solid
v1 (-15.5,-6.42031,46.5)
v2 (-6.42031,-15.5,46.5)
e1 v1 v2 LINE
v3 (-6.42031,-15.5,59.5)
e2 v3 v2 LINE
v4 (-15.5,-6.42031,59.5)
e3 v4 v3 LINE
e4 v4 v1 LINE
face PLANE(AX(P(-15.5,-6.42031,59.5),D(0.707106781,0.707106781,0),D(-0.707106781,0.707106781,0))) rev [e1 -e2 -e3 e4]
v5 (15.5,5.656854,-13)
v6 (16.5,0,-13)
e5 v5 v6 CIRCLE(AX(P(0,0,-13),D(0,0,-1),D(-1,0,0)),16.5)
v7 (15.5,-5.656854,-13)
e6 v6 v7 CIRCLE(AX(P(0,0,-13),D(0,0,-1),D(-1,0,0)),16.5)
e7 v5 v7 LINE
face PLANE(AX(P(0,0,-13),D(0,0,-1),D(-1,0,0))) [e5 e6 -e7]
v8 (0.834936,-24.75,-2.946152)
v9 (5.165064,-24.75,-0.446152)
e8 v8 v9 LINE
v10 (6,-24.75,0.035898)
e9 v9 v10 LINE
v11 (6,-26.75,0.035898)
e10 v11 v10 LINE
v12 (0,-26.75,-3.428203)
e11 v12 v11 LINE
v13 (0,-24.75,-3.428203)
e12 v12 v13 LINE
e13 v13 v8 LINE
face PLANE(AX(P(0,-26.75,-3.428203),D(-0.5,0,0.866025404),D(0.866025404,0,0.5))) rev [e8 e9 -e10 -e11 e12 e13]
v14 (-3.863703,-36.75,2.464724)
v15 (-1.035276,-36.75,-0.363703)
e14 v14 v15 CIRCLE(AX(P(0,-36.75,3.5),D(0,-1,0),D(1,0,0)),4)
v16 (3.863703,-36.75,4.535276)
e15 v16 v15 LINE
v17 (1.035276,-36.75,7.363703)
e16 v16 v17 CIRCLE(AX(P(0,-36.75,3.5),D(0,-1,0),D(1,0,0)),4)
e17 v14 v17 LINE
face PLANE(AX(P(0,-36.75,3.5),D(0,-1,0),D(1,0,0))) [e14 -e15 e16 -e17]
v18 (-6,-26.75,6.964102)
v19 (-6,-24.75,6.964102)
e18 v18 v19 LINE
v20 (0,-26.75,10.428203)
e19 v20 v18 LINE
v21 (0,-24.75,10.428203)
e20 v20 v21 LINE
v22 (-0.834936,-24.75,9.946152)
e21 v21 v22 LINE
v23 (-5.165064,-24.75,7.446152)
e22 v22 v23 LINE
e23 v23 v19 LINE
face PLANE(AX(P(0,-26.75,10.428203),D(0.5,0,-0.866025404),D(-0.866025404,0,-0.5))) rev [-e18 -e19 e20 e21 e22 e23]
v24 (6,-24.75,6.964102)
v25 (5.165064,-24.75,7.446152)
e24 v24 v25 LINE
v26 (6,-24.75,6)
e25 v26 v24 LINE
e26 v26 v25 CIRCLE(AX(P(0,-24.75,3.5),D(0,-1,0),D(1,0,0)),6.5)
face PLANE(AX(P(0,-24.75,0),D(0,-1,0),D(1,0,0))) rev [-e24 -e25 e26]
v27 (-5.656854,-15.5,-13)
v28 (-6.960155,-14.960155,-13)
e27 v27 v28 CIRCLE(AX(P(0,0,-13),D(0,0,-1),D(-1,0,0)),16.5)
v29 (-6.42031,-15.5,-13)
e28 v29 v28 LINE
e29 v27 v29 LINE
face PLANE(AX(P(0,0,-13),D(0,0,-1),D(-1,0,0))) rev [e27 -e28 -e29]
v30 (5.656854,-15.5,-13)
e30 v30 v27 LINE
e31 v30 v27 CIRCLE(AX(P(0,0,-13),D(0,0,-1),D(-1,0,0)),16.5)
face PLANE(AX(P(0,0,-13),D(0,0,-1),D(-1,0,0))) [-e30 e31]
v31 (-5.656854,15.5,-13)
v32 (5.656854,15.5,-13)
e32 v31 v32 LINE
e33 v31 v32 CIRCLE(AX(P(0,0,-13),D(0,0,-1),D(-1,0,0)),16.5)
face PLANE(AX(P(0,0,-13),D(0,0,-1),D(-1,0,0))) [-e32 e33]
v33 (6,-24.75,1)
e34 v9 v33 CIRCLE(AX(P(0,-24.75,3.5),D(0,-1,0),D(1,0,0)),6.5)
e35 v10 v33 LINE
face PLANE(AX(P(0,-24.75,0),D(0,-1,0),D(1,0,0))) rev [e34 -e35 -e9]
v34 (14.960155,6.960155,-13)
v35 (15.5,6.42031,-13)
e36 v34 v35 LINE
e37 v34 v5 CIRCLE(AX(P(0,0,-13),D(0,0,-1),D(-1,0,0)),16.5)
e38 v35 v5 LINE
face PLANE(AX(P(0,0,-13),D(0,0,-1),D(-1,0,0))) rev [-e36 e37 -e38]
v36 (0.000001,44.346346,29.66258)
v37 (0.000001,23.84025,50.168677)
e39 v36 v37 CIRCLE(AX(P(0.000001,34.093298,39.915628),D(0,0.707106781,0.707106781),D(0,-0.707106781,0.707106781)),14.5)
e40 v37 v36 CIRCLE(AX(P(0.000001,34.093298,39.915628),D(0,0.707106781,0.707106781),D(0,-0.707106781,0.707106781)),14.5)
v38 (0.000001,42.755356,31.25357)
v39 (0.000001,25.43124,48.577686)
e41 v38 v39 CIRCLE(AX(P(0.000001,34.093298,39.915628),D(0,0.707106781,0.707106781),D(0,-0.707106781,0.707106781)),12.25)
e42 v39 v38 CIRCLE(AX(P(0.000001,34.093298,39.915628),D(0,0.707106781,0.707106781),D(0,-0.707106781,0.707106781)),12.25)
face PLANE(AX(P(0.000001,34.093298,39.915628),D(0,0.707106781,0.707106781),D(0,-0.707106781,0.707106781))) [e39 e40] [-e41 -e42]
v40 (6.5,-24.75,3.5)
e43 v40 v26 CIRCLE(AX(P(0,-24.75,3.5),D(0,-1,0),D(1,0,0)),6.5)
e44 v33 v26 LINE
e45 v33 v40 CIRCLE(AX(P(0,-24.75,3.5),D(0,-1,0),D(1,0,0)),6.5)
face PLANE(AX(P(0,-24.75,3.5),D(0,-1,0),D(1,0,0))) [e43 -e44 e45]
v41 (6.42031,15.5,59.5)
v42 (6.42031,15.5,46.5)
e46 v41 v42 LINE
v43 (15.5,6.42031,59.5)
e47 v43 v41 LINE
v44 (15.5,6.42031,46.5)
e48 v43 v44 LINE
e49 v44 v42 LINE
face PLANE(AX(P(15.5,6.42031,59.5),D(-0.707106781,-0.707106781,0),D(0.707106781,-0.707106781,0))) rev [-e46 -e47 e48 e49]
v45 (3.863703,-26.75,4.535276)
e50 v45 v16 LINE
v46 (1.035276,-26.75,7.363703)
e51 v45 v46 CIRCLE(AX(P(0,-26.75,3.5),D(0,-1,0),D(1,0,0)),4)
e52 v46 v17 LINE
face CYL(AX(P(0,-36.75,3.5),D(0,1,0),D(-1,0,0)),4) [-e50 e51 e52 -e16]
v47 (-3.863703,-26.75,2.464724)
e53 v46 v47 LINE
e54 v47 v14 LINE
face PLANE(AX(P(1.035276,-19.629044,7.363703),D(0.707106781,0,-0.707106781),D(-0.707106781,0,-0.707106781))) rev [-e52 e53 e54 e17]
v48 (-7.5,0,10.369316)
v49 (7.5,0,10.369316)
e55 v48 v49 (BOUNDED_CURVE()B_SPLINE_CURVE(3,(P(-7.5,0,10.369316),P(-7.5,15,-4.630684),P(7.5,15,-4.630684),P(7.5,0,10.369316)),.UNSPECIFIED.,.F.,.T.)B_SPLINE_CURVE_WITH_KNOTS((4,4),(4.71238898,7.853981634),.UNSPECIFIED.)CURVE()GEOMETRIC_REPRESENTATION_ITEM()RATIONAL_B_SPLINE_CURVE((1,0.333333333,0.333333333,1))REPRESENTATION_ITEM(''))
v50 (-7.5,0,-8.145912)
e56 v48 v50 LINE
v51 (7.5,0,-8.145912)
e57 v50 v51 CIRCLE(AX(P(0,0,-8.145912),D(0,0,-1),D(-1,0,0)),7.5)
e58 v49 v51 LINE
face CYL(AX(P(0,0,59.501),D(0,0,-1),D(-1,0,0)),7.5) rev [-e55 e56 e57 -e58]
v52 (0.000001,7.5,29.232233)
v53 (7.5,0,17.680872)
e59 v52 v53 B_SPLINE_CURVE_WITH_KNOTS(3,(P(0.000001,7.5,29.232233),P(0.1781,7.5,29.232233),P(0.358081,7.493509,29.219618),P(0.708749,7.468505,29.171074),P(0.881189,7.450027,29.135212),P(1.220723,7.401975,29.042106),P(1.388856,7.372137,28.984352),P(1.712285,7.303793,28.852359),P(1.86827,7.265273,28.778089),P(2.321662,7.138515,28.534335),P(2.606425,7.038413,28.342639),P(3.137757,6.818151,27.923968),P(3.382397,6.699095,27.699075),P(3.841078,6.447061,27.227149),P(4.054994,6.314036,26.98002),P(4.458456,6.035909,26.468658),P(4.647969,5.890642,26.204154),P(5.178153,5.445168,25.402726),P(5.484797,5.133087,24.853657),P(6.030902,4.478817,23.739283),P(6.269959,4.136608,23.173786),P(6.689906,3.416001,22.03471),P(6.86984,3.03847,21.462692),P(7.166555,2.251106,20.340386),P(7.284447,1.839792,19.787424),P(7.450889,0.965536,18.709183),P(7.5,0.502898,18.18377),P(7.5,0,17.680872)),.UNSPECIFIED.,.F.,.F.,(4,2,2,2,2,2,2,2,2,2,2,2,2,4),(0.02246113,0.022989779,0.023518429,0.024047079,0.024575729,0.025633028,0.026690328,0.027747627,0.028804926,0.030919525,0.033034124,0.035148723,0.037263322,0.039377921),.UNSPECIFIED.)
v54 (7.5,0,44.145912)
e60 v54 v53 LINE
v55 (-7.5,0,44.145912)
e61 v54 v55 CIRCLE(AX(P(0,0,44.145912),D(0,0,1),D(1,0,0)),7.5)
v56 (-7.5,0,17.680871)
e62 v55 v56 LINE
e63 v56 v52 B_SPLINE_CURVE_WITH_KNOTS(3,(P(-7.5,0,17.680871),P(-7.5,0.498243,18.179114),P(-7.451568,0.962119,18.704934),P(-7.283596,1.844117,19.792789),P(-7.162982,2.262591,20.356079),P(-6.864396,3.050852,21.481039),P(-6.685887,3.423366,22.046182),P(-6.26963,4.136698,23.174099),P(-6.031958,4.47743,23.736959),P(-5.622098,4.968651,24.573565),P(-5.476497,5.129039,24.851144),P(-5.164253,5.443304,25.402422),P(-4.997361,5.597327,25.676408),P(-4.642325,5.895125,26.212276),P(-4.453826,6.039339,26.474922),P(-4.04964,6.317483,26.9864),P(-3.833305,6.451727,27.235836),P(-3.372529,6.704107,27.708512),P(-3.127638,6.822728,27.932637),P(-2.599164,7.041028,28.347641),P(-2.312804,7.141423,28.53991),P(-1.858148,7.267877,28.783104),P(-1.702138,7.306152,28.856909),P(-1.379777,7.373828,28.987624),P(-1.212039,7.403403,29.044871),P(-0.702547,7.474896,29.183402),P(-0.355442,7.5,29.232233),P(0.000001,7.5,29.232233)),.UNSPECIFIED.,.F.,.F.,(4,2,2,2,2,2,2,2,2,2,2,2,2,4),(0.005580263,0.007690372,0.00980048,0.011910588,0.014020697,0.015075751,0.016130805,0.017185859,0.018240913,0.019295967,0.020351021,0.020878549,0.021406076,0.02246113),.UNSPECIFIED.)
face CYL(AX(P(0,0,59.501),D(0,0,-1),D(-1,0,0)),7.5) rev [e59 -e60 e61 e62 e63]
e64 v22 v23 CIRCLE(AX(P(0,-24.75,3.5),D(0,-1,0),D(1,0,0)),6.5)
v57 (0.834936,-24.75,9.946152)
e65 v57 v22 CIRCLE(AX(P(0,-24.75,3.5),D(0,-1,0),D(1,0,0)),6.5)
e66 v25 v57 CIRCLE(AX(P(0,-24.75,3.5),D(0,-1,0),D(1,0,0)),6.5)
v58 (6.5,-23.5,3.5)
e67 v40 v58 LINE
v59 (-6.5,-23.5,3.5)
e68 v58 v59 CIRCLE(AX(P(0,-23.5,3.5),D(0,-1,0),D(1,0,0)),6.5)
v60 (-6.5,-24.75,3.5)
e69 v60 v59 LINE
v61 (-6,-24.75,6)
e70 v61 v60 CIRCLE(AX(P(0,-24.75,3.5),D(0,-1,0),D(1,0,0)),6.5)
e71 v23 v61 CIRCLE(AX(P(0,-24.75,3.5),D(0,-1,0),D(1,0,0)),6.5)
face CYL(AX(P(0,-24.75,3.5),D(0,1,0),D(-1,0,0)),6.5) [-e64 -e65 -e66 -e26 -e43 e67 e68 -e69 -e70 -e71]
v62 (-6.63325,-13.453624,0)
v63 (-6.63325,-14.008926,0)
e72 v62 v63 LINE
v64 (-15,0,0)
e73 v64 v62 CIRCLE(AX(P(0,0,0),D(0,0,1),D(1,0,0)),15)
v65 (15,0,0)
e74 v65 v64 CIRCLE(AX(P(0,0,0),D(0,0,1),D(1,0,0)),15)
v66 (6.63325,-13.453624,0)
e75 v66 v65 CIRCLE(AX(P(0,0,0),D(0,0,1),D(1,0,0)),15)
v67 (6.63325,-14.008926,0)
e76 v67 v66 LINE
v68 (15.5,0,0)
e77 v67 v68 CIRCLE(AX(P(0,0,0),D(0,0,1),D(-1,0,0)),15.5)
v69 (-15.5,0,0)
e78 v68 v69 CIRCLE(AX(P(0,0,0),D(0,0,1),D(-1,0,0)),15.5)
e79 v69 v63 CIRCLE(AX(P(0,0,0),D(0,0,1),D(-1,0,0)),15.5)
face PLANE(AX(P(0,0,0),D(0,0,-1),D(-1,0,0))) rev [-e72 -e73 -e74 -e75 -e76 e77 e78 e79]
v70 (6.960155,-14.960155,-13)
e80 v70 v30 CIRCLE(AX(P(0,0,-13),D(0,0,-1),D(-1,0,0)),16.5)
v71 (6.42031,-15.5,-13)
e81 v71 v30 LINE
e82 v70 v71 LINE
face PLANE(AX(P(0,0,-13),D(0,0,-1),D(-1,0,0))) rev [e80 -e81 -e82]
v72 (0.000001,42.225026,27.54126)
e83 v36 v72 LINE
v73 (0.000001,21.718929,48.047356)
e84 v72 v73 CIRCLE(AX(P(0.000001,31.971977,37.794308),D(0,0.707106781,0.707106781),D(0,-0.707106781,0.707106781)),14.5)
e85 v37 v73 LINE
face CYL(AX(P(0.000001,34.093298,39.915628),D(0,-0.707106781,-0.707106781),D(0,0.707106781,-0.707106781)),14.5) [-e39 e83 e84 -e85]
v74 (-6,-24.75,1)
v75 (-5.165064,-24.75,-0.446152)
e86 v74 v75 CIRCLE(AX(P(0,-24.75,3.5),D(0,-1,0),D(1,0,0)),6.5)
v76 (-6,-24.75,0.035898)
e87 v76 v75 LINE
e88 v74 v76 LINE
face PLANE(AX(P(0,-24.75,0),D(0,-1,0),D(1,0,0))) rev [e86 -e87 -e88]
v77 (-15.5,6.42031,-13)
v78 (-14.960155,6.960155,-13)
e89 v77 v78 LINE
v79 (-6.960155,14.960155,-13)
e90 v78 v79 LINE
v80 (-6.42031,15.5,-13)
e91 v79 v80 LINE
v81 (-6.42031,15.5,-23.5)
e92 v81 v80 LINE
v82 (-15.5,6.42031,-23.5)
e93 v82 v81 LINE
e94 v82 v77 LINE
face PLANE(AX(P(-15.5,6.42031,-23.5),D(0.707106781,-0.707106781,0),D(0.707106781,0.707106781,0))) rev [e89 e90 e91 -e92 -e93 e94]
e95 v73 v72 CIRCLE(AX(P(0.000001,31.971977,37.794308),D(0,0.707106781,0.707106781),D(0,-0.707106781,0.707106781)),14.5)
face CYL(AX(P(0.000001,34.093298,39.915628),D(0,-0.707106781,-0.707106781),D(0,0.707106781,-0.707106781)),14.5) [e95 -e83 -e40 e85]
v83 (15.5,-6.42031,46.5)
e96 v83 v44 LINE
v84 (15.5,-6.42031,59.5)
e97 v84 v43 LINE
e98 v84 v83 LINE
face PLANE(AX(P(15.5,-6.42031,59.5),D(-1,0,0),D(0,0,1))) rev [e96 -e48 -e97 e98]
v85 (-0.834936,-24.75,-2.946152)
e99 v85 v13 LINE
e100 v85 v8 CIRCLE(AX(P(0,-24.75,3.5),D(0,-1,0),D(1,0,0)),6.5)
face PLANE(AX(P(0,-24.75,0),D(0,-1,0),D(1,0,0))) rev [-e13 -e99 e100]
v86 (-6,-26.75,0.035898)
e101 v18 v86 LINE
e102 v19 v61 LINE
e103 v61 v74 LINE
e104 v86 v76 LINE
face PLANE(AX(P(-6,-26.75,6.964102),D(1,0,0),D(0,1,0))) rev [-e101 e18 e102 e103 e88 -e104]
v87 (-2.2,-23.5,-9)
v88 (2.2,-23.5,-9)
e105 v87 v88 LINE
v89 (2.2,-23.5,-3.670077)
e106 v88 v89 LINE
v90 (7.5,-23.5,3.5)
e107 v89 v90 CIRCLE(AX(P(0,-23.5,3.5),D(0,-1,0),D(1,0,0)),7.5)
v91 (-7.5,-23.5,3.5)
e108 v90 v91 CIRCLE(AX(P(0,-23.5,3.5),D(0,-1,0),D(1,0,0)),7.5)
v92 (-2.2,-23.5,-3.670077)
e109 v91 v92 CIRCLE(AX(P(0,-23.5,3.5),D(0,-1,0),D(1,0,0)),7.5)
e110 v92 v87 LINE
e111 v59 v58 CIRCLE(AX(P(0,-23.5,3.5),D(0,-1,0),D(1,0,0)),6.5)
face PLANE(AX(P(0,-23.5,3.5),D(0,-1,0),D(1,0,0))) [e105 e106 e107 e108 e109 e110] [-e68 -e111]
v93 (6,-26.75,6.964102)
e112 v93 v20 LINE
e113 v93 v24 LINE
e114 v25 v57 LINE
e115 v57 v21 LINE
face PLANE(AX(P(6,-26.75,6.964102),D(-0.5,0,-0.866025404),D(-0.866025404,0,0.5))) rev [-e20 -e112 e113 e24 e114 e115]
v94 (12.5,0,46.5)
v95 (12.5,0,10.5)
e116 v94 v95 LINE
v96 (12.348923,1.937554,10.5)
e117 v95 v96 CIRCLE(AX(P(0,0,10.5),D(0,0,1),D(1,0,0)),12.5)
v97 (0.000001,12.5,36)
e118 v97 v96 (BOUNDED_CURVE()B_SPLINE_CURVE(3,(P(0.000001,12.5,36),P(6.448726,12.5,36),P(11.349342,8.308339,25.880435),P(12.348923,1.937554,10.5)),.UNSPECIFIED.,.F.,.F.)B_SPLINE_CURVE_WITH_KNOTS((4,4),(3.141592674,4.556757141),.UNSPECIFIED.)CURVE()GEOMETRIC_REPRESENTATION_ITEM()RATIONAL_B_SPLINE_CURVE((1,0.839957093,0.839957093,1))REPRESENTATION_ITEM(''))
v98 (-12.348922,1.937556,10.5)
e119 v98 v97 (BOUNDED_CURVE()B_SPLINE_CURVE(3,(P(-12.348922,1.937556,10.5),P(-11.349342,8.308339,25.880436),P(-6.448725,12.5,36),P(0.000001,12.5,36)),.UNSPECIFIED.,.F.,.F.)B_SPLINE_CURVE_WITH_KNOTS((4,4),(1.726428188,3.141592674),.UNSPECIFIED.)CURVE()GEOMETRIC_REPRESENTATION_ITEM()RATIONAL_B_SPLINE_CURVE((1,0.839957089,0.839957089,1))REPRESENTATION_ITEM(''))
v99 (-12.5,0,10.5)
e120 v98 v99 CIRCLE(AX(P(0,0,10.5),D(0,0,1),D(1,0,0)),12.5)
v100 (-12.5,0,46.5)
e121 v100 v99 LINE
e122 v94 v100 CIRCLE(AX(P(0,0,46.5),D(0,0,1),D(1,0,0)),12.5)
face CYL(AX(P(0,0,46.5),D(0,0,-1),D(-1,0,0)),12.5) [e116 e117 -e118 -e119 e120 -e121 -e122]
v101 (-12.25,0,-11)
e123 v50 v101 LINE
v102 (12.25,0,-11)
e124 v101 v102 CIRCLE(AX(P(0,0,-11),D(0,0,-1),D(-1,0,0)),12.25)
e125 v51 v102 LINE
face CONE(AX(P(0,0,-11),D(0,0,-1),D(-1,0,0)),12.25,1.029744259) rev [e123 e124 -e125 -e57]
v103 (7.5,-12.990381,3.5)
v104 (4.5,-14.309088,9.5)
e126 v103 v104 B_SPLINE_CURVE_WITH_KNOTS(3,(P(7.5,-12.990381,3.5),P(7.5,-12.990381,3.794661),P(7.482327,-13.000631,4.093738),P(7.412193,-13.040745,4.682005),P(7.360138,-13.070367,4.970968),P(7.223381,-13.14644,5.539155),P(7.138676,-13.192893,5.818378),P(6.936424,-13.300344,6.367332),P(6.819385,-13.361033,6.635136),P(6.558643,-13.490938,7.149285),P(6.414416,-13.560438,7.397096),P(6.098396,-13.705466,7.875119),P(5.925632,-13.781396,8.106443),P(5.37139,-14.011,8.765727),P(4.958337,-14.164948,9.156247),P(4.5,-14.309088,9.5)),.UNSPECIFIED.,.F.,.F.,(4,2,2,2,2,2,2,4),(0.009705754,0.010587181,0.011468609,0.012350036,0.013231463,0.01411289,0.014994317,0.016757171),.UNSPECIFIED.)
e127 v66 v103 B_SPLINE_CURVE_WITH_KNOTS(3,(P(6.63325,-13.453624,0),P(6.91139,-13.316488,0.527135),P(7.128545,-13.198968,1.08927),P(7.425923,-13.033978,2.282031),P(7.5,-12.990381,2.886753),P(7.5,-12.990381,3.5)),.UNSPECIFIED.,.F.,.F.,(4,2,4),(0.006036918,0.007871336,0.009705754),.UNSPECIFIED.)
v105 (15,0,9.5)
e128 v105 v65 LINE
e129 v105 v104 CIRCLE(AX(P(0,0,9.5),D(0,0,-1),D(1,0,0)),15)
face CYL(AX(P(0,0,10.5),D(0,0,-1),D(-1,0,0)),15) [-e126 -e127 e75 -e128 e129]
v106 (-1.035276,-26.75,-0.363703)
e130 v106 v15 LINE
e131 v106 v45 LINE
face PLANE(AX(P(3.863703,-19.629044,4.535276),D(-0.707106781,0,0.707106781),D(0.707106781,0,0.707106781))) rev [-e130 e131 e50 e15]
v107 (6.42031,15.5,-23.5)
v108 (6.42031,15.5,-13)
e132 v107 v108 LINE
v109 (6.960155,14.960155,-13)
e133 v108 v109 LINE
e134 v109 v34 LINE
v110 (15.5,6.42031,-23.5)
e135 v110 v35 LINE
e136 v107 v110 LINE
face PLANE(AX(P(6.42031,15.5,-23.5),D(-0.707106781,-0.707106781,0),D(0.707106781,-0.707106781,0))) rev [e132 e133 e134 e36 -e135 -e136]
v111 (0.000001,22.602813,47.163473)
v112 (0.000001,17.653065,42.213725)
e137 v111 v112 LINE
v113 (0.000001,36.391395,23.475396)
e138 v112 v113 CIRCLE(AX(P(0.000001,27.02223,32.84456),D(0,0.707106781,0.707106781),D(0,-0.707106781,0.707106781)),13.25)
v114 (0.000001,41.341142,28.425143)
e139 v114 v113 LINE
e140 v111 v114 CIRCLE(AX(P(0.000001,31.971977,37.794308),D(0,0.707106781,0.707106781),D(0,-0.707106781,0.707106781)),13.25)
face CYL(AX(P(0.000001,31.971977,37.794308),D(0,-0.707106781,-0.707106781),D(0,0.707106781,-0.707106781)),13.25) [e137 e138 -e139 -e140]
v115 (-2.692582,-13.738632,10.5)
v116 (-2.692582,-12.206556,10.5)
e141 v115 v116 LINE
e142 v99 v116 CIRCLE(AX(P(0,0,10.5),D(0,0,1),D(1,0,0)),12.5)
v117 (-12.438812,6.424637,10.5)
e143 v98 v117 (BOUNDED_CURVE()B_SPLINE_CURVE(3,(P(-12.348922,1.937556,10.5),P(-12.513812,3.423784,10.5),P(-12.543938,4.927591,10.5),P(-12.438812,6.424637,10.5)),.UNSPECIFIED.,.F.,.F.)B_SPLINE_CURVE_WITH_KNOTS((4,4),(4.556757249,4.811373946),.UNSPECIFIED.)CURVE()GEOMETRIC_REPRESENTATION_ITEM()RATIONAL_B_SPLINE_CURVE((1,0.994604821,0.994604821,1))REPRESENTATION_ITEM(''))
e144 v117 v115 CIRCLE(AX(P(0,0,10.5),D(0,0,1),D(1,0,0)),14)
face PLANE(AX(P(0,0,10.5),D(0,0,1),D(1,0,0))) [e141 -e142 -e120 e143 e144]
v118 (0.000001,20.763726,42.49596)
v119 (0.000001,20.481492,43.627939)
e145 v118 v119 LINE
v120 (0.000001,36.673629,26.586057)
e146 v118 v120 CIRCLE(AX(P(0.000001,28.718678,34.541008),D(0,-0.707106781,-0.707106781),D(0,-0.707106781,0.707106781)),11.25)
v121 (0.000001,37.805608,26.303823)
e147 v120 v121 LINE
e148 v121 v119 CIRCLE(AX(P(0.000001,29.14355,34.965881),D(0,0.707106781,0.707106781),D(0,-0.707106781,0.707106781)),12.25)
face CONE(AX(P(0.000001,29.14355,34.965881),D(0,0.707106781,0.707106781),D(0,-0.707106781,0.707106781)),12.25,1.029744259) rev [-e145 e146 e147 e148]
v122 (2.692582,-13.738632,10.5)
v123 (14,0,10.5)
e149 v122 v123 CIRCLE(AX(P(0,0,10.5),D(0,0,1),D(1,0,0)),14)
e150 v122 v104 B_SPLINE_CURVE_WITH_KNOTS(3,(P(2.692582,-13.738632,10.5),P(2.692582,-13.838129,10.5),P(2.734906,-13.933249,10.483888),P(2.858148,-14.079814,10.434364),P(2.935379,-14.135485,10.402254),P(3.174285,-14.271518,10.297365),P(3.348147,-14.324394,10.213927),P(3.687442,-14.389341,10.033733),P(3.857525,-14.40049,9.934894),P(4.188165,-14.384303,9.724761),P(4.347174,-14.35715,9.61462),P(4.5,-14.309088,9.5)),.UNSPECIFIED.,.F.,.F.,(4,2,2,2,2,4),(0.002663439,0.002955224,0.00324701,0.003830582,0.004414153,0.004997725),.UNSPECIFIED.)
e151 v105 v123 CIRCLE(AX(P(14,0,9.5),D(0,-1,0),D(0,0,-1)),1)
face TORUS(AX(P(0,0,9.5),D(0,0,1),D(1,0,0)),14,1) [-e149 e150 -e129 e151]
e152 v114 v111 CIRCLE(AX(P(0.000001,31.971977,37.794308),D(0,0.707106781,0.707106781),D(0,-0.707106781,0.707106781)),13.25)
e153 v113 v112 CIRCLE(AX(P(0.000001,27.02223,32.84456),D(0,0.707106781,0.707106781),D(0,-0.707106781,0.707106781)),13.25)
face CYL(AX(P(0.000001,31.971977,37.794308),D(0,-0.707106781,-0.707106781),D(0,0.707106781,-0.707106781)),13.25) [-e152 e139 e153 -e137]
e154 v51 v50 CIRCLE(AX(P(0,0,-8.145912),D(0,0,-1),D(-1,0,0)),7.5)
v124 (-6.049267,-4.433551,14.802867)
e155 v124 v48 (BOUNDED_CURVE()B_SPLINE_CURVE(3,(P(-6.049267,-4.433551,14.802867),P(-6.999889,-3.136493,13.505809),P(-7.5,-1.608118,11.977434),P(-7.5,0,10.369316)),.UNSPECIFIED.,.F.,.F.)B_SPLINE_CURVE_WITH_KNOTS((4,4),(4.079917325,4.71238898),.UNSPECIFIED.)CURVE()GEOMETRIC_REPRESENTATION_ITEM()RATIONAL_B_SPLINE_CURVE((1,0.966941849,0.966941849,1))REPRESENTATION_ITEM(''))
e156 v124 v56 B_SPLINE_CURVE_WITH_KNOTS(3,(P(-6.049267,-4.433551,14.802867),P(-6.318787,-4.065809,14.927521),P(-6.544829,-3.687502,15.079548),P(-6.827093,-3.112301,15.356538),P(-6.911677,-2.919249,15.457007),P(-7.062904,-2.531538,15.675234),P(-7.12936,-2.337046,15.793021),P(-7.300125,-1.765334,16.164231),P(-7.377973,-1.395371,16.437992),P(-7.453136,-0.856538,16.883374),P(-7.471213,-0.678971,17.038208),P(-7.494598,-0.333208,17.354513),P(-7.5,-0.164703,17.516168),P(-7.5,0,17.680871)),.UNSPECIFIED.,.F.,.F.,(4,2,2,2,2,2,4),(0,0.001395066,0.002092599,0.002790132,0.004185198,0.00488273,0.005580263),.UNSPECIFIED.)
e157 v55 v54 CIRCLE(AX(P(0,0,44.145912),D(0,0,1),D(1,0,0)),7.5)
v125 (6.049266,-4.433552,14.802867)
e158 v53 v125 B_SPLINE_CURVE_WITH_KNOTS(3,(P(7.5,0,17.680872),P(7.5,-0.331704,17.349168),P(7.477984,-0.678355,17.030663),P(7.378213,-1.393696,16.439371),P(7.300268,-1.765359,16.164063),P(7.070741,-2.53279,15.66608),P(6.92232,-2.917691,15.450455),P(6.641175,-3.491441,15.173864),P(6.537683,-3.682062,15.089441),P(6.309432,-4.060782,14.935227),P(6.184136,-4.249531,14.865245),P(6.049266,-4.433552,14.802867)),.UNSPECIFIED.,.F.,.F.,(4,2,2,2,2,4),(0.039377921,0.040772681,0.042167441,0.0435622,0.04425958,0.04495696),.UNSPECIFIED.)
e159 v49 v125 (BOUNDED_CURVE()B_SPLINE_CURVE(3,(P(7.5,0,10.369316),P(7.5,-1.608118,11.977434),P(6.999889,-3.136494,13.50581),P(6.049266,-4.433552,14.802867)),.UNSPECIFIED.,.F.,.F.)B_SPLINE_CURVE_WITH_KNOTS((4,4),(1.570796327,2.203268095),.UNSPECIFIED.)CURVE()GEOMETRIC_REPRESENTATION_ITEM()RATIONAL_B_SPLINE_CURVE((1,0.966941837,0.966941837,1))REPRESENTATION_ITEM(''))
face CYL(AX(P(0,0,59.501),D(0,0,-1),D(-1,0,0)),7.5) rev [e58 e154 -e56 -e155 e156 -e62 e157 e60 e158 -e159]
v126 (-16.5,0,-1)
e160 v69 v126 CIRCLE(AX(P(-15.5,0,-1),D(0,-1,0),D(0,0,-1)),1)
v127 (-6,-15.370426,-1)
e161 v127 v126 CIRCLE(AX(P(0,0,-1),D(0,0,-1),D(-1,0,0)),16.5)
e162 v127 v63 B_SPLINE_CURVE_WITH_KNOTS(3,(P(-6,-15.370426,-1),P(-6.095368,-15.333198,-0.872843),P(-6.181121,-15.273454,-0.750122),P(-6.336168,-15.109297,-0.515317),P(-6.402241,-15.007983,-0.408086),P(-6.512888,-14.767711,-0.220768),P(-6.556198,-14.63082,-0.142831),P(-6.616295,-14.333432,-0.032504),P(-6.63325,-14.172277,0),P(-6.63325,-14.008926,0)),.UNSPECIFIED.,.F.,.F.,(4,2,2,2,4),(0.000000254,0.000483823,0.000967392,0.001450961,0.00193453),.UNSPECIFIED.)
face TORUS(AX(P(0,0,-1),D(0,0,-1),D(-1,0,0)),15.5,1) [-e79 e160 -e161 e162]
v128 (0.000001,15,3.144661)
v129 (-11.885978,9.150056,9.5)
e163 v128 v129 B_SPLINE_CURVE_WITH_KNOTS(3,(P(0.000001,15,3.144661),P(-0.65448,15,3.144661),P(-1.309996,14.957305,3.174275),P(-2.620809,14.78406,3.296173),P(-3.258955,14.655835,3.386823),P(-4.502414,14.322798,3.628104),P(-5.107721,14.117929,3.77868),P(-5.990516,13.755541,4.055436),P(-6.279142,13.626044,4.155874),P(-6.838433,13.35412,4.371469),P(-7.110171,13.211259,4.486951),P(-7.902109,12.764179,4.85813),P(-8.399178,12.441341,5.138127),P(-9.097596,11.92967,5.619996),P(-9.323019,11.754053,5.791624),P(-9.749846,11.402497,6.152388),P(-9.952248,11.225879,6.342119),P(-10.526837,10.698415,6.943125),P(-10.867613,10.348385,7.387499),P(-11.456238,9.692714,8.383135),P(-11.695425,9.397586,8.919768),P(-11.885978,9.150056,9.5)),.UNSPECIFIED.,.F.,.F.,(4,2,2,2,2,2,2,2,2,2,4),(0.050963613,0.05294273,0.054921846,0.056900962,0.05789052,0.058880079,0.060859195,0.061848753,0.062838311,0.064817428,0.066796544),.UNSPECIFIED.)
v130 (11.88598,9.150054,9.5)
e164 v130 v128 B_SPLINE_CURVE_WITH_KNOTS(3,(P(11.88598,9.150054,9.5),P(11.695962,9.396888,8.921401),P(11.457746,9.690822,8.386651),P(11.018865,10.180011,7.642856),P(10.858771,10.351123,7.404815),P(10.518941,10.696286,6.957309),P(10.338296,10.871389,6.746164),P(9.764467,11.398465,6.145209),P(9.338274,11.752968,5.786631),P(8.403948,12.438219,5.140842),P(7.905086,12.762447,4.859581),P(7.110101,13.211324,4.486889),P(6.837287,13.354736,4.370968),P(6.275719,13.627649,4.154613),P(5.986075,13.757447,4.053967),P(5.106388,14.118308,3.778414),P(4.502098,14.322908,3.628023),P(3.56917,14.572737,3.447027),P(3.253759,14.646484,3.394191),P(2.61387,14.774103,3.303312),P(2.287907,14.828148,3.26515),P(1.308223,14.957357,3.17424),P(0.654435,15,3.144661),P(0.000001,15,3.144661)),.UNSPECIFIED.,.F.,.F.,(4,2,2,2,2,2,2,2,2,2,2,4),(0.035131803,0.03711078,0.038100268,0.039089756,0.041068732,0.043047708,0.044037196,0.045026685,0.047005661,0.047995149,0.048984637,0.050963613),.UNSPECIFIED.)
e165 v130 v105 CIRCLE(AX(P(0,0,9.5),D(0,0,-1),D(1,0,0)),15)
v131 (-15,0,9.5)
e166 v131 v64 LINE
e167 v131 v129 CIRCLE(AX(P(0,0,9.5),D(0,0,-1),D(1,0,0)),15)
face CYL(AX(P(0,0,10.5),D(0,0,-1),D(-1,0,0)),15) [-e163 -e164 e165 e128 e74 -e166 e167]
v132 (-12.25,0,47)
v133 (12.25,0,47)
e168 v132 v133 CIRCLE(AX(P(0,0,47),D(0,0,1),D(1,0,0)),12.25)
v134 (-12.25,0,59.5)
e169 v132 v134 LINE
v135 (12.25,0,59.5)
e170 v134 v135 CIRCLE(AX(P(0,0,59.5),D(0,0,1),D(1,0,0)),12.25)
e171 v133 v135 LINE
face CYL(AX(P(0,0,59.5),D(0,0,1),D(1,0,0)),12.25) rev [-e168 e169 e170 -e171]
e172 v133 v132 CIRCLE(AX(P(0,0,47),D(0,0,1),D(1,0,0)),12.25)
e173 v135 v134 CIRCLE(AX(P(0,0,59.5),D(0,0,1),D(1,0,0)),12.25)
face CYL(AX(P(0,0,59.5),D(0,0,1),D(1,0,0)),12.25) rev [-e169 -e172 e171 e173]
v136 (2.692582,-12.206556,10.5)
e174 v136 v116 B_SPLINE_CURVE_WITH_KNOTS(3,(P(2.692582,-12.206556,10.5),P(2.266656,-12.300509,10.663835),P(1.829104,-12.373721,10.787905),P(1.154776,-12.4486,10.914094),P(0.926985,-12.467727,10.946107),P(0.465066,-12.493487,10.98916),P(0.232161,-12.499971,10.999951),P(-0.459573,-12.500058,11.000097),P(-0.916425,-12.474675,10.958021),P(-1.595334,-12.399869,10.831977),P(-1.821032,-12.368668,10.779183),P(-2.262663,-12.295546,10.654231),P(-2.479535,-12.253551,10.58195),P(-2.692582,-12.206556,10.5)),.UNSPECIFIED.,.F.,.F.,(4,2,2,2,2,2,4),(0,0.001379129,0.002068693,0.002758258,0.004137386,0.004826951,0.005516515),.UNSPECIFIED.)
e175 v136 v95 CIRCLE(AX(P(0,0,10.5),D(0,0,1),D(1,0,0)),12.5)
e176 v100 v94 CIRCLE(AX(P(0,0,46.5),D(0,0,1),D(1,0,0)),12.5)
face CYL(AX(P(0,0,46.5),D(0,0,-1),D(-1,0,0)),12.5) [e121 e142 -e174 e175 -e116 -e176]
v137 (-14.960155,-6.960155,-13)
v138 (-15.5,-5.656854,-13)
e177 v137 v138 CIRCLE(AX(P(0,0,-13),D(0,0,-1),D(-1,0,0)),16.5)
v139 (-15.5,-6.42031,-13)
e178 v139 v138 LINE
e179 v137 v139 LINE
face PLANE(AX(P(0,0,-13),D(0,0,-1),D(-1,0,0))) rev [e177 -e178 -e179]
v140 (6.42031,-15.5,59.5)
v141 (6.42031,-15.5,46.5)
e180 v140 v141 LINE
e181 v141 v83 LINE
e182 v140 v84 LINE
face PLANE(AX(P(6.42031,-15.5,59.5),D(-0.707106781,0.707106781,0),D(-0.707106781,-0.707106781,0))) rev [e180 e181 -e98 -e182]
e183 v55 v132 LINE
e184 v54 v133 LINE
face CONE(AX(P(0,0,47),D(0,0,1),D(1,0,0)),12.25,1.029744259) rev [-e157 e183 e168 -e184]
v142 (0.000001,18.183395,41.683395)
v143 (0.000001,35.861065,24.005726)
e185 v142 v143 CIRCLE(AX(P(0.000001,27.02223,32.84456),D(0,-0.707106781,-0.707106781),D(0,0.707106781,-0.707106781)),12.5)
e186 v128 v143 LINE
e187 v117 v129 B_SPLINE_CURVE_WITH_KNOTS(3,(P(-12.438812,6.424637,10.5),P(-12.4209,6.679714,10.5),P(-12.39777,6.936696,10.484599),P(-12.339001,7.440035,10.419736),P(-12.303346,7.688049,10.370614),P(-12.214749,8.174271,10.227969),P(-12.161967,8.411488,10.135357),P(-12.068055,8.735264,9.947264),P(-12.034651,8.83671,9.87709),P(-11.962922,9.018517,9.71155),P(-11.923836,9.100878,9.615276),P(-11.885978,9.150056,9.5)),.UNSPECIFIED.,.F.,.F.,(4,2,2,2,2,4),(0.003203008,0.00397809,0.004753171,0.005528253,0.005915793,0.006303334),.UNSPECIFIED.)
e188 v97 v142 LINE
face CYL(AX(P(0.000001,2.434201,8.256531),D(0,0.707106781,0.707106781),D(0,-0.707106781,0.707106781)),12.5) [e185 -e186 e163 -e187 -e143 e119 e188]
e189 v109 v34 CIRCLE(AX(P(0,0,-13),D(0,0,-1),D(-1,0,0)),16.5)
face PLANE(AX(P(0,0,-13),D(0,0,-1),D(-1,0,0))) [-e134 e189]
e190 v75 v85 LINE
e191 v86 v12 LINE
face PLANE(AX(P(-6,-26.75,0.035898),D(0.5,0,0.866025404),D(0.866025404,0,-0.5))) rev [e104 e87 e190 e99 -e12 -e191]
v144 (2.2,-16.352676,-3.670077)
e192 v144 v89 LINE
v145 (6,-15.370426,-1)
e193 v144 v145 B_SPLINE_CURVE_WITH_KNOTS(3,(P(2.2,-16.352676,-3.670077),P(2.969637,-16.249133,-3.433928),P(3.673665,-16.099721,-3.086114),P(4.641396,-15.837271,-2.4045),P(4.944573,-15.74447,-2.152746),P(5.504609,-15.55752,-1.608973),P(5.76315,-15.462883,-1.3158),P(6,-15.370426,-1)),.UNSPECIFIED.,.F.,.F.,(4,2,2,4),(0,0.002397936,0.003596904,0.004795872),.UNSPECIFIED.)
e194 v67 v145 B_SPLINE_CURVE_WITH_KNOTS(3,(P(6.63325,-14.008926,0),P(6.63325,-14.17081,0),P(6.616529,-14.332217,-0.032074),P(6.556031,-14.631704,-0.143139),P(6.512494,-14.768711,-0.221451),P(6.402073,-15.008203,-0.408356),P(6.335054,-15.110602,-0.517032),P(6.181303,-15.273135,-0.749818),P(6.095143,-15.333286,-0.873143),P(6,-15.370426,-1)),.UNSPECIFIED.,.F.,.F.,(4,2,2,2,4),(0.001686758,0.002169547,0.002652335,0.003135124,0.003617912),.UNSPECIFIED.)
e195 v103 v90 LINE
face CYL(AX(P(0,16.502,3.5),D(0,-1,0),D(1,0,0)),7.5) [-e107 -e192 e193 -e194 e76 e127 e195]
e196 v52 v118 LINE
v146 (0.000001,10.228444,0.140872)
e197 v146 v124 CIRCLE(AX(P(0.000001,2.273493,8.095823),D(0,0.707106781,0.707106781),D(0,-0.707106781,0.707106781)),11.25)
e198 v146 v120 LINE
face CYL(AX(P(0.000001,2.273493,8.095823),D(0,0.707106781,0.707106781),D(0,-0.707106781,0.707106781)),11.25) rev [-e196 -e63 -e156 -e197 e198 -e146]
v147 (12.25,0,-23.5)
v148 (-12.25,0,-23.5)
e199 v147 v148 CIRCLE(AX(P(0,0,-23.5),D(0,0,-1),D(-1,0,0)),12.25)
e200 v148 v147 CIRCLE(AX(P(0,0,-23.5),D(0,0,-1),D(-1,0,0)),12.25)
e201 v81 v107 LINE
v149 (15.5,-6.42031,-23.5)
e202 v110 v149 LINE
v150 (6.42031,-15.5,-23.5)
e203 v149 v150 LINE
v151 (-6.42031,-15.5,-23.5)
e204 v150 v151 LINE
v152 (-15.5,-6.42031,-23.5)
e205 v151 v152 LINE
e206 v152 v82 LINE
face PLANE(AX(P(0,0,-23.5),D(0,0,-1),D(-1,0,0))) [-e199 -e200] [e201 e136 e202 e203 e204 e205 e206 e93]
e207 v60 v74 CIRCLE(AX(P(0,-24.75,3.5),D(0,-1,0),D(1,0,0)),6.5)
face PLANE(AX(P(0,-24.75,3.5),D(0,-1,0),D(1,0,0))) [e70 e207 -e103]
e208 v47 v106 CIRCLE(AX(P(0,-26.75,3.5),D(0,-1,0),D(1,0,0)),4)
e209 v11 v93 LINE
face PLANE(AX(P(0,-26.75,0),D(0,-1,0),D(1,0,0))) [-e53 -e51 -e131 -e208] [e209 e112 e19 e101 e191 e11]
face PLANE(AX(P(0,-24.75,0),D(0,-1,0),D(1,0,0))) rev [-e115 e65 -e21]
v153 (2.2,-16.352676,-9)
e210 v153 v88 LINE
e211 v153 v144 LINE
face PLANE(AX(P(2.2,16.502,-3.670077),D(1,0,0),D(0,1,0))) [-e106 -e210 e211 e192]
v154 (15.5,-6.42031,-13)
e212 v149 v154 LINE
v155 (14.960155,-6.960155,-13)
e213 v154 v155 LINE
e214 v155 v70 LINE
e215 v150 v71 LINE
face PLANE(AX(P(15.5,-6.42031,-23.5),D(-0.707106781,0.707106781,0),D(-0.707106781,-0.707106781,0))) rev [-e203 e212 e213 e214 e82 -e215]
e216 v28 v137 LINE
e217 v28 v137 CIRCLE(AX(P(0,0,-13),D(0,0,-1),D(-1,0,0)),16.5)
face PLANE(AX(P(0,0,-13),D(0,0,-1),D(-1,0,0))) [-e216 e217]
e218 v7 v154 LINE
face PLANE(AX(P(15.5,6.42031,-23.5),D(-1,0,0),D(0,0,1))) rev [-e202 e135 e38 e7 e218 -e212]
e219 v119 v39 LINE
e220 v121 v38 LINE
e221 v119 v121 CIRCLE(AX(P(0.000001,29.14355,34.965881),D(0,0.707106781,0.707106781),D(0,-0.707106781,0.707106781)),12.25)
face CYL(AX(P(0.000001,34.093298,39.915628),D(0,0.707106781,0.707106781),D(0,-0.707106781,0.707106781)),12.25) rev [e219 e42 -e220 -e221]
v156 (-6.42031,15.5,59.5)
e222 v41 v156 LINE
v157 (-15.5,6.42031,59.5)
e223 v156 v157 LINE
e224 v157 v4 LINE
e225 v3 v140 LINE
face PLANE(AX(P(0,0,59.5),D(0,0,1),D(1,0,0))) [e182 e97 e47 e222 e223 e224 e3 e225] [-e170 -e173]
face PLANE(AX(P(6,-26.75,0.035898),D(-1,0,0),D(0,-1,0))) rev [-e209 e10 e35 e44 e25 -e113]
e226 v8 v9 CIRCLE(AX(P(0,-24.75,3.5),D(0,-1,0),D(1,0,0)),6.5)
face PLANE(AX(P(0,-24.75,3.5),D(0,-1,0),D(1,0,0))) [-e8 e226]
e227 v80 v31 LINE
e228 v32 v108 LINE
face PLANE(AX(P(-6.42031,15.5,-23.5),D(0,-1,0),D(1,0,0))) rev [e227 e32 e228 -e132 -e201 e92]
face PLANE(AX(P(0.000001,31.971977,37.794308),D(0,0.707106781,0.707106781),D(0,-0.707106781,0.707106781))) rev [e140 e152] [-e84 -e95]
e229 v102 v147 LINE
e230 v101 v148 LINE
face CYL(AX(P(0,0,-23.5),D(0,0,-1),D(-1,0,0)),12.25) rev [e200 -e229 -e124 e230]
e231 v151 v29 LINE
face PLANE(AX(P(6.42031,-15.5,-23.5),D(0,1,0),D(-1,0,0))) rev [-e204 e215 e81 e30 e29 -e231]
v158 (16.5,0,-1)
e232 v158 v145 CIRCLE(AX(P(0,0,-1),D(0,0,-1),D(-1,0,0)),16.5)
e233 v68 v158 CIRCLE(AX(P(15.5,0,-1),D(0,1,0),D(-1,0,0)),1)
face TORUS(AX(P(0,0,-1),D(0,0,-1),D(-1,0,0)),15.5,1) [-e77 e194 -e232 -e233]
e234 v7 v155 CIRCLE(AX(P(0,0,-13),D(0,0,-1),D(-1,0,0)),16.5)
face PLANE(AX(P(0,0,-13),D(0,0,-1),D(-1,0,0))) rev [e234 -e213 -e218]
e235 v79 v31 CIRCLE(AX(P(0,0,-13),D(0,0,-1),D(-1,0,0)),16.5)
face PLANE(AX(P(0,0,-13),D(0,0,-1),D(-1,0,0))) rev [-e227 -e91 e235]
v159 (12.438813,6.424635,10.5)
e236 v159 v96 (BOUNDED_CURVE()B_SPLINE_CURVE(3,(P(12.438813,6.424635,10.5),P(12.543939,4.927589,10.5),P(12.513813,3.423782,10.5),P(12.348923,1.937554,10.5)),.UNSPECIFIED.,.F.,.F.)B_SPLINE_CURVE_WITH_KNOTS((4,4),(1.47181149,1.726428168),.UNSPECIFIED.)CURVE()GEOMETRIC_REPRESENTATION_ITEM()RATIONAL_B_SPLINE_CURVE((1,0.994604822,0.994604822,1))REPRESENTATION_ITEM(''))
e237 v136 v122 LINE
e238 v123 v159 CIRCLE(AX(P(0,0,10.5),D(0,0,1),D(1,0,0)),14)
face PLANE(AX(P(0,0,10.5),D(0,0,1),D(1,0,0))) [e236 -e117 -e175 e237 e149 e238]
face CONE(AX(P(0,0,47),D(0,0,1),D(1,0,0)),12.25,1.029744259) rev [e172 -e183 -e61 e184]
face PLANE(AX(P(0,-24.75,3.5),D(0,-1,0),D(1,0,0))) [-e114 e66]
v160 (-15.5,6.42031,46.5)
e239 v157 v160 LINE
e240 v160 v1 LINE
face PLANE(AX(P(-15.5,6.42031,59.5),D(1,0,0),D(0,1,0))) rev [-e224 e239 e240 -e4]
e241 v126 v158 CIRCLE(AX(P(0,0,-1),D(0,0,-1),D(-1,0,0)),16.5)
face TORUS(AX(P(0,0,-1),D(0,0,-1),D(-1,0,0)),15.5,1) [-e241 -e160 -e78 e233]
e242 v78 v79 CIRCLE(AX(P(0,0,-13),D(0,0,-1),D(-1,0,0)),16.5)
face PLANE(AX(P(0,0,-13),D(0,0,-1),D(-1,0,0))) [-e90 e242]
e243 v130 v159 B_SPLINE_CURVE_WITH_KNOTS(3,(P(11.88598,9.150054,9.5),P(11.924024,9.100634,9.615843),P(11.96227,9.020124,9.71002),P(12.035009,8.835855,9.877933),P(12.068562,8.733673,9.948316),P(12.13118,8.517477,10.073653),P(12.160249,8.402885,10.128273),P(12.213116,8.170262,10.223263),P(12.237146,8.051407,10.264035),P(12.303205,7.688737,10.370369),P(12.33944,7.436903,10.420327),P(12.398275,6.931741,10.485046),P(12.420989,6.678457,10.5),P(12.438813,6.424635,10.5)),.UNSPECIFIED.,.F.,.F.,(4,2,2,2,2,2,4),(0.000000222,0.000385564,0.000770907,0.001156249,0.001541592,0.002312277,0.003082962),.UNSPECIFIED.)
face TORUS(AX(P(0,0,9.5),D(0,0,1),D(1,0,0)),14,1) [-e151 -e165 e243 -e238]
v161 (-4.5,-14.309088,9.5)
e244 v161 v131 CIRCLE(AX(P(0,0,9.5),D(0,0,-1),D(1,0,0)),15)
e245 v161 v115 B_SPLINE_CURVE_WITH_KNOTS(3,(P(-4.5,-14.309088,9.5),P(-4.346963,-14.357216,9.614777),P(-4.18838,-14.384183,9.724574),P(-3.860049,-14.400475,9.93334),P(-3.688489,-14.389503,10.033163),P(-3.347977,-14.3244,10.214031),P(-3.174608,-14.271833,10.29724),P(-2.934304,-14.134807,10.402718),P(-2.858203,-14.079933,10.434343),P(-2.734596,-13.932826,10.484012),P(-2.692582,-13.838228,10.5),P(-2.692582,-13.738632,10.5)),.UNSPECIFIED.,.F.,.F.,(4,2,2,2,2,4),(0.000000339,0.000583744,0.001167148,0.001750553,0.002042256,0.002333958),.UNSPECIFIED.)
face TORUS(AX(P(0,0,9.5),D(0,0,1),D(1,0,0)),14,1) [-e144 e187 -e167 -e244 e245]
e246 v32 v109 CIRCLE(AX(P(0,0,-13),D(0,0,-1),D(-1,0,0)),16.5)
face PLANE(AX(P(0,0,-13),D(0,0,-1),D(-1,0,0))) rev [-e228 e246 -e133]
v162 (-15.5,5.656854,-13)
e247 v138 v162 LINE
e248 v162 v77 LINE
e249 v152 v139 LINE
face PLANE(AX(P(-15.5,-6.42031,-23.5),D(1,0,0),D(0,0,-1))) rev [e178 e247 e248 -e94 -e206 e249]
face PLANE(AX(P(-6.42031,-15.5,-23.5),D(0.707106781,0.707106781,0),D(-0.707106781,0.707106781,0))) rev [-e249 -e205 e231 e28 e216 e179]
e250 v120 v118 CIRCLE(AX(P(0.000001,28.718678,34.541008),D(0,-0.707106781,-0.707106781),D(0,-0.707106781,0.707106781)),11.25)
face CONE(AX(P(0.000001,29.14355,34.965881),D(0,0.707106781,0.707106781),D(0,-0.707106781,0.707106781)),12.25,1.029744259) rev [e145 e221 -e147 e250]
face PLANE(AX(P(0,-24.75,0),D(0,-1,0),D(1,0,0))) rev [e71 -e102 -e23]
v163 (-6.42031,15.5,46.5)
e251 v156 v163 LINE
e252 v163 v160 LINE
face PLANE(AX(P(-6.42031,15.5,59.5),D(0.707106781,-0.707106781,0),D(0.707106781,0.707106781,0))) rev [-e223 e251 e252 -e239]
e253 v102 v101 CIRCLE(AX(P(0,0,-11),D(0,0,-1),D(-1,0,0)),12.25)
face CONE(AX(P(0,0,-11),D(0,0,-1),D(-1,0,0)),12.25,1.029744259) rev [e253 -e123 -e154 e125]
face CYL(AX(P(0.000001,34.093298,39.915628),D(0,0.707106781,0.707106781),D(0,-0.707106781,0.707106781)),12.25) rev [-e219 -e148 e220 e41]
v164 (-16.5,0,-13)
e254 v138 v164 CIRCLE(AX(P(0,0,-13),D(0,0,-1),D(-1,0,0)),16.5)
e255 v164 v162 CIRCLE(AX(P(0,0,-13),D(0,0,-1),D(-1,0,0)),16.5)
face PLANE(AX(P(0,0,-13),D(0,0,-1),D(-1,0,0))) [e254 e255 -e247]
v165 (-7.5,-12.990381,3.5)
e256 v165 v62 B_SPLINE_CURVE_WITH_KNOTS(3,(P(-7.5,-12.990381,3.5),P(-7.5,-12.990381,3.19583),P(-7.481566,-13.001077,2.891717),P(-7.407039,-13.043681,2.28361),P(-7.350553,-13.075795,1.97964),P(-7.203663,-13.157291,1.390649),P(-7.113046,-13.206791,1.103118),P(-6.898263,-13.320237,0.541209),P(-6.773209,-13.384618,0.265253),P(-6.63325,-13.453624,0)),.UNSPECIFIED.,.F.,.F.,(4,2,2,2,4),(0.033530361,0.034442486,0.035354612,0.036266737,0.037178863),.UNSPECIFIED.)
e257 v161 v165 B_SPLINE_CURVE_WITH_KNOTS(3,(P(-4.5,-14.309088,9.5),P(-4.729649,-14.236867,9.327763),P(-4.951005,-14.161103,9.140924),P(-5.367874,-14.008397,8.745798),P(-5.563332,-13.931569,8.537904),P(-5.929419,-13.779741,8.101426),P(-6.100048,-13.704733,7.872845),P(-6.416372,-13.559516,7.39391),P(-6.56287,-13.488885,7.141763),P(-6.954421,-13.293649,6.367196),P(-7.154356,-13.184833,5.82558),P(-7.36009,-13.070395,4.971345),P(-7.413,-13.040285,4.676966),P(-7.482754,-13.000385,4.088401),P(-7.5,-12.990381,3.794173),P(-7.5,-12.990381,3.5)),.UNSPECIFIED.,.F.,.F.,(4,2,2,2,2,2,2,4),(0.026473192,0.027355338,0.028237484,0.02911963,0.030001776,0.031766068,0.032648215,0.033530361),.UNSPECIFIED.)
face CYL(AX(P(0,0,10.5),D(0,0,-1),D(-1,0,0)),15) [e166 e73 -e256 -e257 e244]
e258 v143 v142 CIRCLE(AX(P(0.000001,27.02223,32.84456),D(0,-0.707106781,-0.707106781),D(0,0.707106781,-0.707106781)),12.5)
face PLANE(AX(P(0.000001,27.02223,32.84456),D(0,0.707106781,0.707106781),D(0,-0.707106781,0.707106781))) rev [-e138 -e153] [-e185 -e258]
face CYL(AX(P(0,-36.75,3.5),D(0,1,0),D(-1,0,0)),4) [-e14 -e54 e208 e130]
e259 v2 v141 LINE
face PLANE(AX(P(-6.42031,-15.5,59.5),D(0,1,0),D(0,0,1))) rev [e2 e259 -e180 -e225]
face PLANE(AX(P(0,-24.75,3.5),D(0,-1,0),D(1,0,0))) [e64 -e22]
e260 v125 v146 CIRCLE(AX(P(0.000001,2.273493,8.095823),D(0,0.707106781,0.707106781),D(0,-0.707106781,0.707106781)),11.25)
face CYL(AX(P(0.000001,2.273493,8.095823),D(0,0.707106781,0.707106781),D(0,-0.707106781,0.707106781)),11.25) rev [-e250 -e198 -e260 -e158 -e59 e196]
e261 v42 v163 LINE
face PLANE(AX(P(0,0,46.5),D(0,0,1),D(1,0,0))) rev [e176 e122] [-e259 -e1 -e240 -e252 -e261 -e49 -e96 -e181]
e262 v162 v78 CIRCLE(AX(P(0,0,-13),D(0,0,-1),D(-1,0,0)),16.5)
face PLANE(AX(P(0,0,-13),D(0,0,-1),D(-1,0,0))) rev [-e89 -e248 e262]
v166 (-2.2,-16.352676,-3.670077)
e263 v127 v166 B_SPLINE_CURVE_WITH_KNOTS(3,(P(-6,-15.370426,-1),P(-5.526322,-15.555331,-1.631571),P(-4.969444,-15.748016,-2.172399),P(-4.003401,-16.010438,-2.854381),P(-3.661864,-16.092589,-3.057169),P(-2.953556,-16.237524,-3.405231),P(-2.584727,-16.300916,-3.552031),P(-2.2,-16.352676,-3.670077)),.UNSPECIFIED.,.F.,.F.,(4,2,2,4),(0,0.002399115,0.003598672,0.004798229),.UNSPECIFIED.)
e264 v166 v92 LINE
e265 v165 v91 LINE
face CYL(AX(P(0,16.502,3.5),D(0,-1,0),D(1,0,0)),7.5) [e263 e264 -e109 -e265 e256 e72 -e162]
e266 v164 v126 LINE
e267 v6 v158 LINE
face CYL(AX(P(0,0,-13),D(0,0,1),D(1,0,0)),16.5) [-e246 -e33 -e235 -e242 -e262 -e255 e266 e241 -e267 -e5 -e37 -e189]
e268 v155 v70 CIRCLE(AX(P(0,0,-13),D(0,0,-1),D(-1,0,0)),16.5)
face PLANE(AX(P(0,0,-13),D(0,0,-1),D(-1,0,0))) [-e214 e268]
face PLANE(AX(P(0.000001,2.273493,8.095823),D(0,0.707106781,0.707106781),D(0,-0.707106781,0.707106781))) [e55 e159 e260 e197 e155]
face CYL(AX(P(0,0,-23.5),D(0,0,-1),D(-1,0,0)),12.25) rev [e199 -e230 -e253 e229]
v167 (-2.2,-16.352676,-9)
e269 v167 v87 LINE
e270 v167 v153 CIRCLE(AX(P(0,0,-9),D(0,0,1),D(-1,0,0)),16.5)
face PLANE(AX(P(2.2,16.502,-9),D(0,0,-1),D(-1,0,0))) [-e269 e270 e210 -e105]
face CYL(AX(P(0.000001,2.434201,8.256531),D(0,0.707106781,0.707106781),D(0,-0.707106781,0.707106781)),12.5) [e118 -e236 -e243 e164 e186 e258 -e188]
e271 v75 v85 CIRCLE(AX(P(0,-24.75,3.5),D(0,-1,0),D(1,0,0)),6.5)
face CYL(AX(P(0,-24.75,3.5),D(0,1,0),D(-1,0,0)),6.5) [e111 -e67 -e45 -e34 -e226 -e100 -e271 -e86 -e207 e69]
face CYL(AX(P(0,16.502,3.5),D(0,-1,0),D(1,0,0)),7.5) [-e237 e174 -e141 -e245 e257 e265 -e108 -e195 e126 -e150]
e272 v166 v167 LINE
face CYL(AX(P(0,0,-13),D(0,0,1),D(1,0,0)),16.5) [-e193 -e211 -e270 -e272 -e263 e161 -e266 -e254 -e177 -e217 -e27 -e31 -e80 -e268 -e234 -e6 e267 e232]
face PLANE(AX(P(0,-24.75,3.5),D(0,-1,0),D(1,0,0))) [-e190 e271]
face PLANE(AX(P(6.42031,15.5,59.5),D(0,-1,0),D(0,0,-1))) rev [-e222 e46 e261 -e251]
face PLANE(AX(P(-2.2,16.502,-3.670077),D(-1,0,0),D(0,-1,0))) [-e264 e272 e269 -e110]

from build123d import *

# Parameters (mm, degrees)
SKETCH_1_R               = 15
EXTRUDE_1_DEPTH          = 10.5
SKETCH_2_R               = 12.5
EXTRUDE_2_DEPTH          = 36
EXTRUDE_3_DEPTH          = 13
SKETCH_4_R               = 16.5
EXTRUDE_4_DEPTH          = 13
EXTRUDE_5_DEPTH          = 10.5
FILLET_1_R               = 1
HOLE_WIZARD_G3_4_1_D     = 24.5
HOLE_WIZARD_G3_4_1_DEPTH = 12.5
HOLE_WIZARD_G3_4_1_TIP   = 7.360542583
HOLE_WIZARD_G3_4_2_D     = 24.5
HOLE_WIZARD_G3_4_2_DEPTH = 12.5
HOLE_WIZARD_G3_4_2_TIP   = 7.360542583
EXTRUDE_6_REACH          = 75.57
SKETCH_13_R              = 6.5
EXTRUDE_7_DEPTH          = 1.25
EXTRUDE_8_DEPTH          = 2
SKETCH_15_R              = 4
EXTRUDE_9_DEPTH          = 10
SKETCH_18_R              = 12.5
SKETCH_19_R              = 13.25
EXTRUDE_10_DEPTH         = 7
SKETCH_20_R              = 14.5
EXTRUDE_11_DEPTH         = 3
HOLE_WIZARD_G3_4_3_D     = 24.5
HOLE_WIZARD_G3_4_3_DEPTH = 7
HOLE_WIZARD_G3_4_3_TIP   = 7.360542583
SKETCH_24_R              = 11.25
CUT_EXTRUDE_2_DEPTH      = 45
CUT_EXTRUDE_1_REACH      = 97.54
SKETCH_11_R              = 7.5
CUT_EXTRUDE_START        = -10
CUT_EXTRUDE_3_DEPTH      = 10


with BuildPart() as part:
    # 草图1 → 凸台-拉伸1 (new body)
    with BuildSketch(Plane.XY):
        with Locations(Location((0, 0, 0), (0, 0, 180))):
            Circle(SKETCH_1_R)
    extrude(amount=EXTRUDE_1_DEPTH)

    # 草图2 → 凸台-拉伸2 (add)
    with BuildSketch(Plane.XY.offset(10.5)):
        Circle(SKETCH_2_R)
    extrude(amount=EXTRUDE_2_DEPTH)

    # 草图3 → 凸台-拉伸3 (add)
    with BuildSketch(Plane.XY.offset(46.5)):
        Polygon((6.420310217, -15.5), (15.5, -6.420310217), (15.5, 6.420310217), (6.420310217, 15.5), (-6.420310217, 15.5), (-15.5, 6.420310217), (-15.5, -6.420310217), (-6.420310217, -15.5), align=None)
    extrude(amount=EXTRUDE_3_DEPTH)

    # 草图4 → 凸台-拉伸4 (add)
    with BuildSketch(Plane(origin=(0, 0, 0), x_dir=(-1, 0, 0), z_dir=(0, 0, -1))):
        with Locations(Location((0, 0, 0), (0, 0, 180))):
            Circle(SKETCH_4_R)
    extrude(amount=EXTRUDE_4_DEPTH)

    # 草图6 → 凸台-拉伸5 (add)
    with BuildSketch(Plane(origin=(0, 0, -13), x_dir=(-1, 0, 0), z_dir=(0, 0, -1))):
        Polygon((15.5, -6.420310217), (15.5, 6.420310217), (6.420310217, 15.5), (-6.420310217, 15.5), (-15.5, 6.420310217), (-15.5, -6.420310217), (-6.420310217, -15.5), (6.420310217, -15.5), align=None)
    extrude(amount=EXTRUDE_5_DEPTH)

    # 圆角1
    fillet_1_edges = [part.edges().sort_by_distance(p)[0] for p in [
        (-16.5, 0, 0),
        (15, 0, 10.5),
    ]]
    fillet(fillet_1_edges, radius=FILLET_1_R)

    # G3/4 螺纹孔1
    with Locations(Plane.XY.offset(59.5)):
        with Locations((0, 0)):
            Hole(HOLE_WIZARD_G3_4_1_D / 2, depth=HOLE_WIZARD_G3_4_1_DEPTH)
            with Locations((0, 0, -(HOLE_WIZARD_G3_4_1_DEPTH + HOLE_WIZARD_G3_4_1_TIP / 2))):  # 118° drill point
                Cone(0, HOLE_WIZARD_G3_4_1_D / 2, HOLE_WIZARD_G3_4_1_TIP, mode=Mode.SUBTRACT)

    # G3/4 螺纹孔2
    with Locations(Plane(origin=(0, 0, -23.5), x_dir=(-1, 0, 0), z_dir=(0, 0, -1))):
        with Locations((0, 0)):
            Hole(HOLE_WIZARD_G3_4_2_D / 2, depth=HOLE_WIZARD_G3_4_2_DEPTH)
            with Locations((0, 0, -(HOLE_WIZARD_G3_4_2_DEPTH + HOLE_WIZARD_G3_4_2_TIP / 2))):  # 118° drill point
                Cone(0, HOLE_WIZARD_G3_4_2_D / 2, HOLE_WIZARD_G3_4_2_TIP, mode=Mode.SUBTRACT)

    # 草图12 → 凸台-拉伸6 (add, up to next)
    with BuildSketch(Plane(origin=(0, -23.5, 0), x_dir=(-1, 0, 0), z_dir=(0, -1, 0)), mode=Mode.PRIVATE) as extrude_6_sk1:
        with BuildLine():
            Line((-2.2, 9), (2.2, 9))
            Line((2.2, 9), (2.2, 3.670076708))
            ThreePointArc((2.2, 3.670076708), (0, -11), (-2.2, 3.670076708))
            Line((-2.2, 3.670076708), (-2.2, 9))
        make_face()
    extrude_6_tool1 = extrude(extrude_6_sk1.sketch, amount=-EXTRUDE_6_REACH, mode=Mode.PRIVATE) - part.part
    add(extrude_6_tool1.solids().sort_by_distance((0, -23.5, 2.377731))[0])

    # 草图13 → 凸台-拉伸7 (add)
    with BuildSketch(Plane.XZ.offset(23.5)):
        with Locations((0, 3.5)):
            Circle(SKETCH_13_R)
    extrude(amount=EXTRUDE_7_DEPTH)

    # 草图14 → 凸台-拉伸8 (add)
    with BuildSketch(Plane.XZ.offset(24.75)):
        Polygon((6, 6.964101615), (0, 10.42820323), (-6, 6.964101615), (-6, 0.035898385), (0, -3.42820323), (6, 0.035898385), align=None)
    extrude(amount=EXTRUDE_8_DEPTH)

    # 草图15 → 凸台-拉伸9 (add)
    with BuildSketch(Plane.XZ.offset(26.75)):
        with Locations((0, 3.5)):
            Circle(SKETCH_15_R)
    extrude(amount=EXTRUDE_9_DEPTH)

    # 扫描2: sweep along a path in 草图16
    with BuildLine(Plane(origin=(0, 0, 0), x_dir=(0, 0, -1), z_dir=(1, 0, 0))) as sweep_2_path:
        Line((-10.530023664, 0.160707832), (-35.118053174, 24.748737342))
    # 草图18 → 扫描2 (sweep)
    with BuildSketch(Plane(origin=(0, 5.345365748, 5.345365748), x_dir=(-0.9999999999999926, -8.68879538818696e-08, 8.688795429591137e-08), z_dir=(0, -0.7071067811865435, -0.7071067811865517))):
        with Locations((0, -4.117009359)):
            Circle(SKETCH_18_R)
    sweep(path=sweep_2_path.line)

    # 草图19 → 凸台-拉伸10 (add)
    with BuildSketch(Plane(origin=(0, 29.933395258, 29.933395258), x_dir=(1, 0, 0), z_dir=(0, 0.7071067811865434, 0.7071067811865517))):
        with Locations(Location((5.06e-07, -4.117009359, 0), (0, 0, 270))):
            Circle(SKETCH_19_R)
    extrude(amount=EXTRUDE_10_DEPTH)

    # 草图20 → 凸台-拉伸11 (add)
    with BuildSketch(Plane(origin=(0, 34.883142726, 34.883142726), x_dir=(1, 0, 0), z_dir=(0, 0.7071067811865434, 0.7071067811865517))):
        with Locations(Location((5.06e-07, -4.117009359, 0), (0, 0, 270))):
            Circle(SKETCH_20_R)
    extrude(amount=EXTRUDE_11_DEPTH)

    # G3/4 螺纹孔3
    with Locations(Plane(origin=(5.06e-07, 34.093297833, 39.915628305), x_dir=(0, 0.707106781187, -0.707106781187), z_dir=(0, 0.707106781187, 0.707106781187))):
        with Locations((0, 0)):
            Hole(HOLE_WIZARD_G3_4_3_D / 2, depth=HOLE_WIZARD_G3_4_3_DEPTH)
            with Locations((0, 0, -(HOLE_WIZARD_G3_4_3_DEPTH + HOLE_WIZARD_G3_4_3_TIP / 2))):  # 118° drill point
                Cone(0, HOLE_WIZARD_G3_4_3_D / 2, HOLE_WIZARD_G3_4_3_TIP, mode=Mode.SUBTRACT)

    # 草图24 → 切除-拉伸2 (cut)
    with BuildSketch(Plane(origin=(0, 37.004463069, 37.004463069), x_dir=(1, 0, 0), z_dir=(0, 0.7071067811865434, 0.7071067811865517))):
        with Locations(Location((5.06e-07, -4.117009359, 0), (0, 0, 270))):
            Circle(SKETCH_24_R)
    extrude(amount=-CUT_EXTRUDE_2_DEPTH, mode=Mode.SUBTRACT)

    # 切除-拉伸1: up to this cone (the profile starts outside it)
    cut_extrude_1_end = Plane(origin=(0, 0, -23.5), z_dir=(0, 0, 1)).offset(63.139458417) * Cone(1.664e-06, 58.084256944, 34.900541583, align=(Align.CENTER, Align.CENTER, Align.MIN), mode=Mode.PRIVATE)
    # 草图11 → 切除-拉伸1 (cut, up to the surface)
    with BuildSketch(Plane(origin=(0, 0, -23.5), x_dir=(-1, 0, 0), z_dir=(0, 0, -1)), mode=Mode.PRIVATE) as cut_extrude_1_sk1:
        Circle(SKETCH_11_R)
    cut_extrude_1_tool1 = extrude(cut_extrude_1_sk1.sketch, amount=-CUT_EXTRUDE_1_REACH, mode=Mode.PRIVATE) - cut_extrude_1_end
    add(cut_extrude_1_tool1.solids().sort_by_distance((0, 0, -23.5))[0], mode=Mode.SUBTRACT)

    # 草图25 → 切除-拉伸3 (cut)
    with BuildSketch(Plane.XZ.offset(36.75).offset(CUT_EXTRUDE_START)):
        with BuildLine():
            Line((1.03527618, 7.363703305), (-3.863703305, 2.46472382))
            ThreePointArc((-3.863703305, 2.46472382), (-2.828427125, 6.328427125), (1.03527618, 7.363703305))
        make_face()
        with BuildLine():
            Line((3.863703305, 4.53527618), (-1.03527618, -0.363703305))
            ThreePointArc((-1.03527618, -0.363703305), (2.828427125, 0.671572875), (3.863703305, 4.53527618))
        make_face()
    extrude(amount=CUT_EXTRUDE_3_DEPTH, mode=Mode.SUBTRACT)


solid = part.part
